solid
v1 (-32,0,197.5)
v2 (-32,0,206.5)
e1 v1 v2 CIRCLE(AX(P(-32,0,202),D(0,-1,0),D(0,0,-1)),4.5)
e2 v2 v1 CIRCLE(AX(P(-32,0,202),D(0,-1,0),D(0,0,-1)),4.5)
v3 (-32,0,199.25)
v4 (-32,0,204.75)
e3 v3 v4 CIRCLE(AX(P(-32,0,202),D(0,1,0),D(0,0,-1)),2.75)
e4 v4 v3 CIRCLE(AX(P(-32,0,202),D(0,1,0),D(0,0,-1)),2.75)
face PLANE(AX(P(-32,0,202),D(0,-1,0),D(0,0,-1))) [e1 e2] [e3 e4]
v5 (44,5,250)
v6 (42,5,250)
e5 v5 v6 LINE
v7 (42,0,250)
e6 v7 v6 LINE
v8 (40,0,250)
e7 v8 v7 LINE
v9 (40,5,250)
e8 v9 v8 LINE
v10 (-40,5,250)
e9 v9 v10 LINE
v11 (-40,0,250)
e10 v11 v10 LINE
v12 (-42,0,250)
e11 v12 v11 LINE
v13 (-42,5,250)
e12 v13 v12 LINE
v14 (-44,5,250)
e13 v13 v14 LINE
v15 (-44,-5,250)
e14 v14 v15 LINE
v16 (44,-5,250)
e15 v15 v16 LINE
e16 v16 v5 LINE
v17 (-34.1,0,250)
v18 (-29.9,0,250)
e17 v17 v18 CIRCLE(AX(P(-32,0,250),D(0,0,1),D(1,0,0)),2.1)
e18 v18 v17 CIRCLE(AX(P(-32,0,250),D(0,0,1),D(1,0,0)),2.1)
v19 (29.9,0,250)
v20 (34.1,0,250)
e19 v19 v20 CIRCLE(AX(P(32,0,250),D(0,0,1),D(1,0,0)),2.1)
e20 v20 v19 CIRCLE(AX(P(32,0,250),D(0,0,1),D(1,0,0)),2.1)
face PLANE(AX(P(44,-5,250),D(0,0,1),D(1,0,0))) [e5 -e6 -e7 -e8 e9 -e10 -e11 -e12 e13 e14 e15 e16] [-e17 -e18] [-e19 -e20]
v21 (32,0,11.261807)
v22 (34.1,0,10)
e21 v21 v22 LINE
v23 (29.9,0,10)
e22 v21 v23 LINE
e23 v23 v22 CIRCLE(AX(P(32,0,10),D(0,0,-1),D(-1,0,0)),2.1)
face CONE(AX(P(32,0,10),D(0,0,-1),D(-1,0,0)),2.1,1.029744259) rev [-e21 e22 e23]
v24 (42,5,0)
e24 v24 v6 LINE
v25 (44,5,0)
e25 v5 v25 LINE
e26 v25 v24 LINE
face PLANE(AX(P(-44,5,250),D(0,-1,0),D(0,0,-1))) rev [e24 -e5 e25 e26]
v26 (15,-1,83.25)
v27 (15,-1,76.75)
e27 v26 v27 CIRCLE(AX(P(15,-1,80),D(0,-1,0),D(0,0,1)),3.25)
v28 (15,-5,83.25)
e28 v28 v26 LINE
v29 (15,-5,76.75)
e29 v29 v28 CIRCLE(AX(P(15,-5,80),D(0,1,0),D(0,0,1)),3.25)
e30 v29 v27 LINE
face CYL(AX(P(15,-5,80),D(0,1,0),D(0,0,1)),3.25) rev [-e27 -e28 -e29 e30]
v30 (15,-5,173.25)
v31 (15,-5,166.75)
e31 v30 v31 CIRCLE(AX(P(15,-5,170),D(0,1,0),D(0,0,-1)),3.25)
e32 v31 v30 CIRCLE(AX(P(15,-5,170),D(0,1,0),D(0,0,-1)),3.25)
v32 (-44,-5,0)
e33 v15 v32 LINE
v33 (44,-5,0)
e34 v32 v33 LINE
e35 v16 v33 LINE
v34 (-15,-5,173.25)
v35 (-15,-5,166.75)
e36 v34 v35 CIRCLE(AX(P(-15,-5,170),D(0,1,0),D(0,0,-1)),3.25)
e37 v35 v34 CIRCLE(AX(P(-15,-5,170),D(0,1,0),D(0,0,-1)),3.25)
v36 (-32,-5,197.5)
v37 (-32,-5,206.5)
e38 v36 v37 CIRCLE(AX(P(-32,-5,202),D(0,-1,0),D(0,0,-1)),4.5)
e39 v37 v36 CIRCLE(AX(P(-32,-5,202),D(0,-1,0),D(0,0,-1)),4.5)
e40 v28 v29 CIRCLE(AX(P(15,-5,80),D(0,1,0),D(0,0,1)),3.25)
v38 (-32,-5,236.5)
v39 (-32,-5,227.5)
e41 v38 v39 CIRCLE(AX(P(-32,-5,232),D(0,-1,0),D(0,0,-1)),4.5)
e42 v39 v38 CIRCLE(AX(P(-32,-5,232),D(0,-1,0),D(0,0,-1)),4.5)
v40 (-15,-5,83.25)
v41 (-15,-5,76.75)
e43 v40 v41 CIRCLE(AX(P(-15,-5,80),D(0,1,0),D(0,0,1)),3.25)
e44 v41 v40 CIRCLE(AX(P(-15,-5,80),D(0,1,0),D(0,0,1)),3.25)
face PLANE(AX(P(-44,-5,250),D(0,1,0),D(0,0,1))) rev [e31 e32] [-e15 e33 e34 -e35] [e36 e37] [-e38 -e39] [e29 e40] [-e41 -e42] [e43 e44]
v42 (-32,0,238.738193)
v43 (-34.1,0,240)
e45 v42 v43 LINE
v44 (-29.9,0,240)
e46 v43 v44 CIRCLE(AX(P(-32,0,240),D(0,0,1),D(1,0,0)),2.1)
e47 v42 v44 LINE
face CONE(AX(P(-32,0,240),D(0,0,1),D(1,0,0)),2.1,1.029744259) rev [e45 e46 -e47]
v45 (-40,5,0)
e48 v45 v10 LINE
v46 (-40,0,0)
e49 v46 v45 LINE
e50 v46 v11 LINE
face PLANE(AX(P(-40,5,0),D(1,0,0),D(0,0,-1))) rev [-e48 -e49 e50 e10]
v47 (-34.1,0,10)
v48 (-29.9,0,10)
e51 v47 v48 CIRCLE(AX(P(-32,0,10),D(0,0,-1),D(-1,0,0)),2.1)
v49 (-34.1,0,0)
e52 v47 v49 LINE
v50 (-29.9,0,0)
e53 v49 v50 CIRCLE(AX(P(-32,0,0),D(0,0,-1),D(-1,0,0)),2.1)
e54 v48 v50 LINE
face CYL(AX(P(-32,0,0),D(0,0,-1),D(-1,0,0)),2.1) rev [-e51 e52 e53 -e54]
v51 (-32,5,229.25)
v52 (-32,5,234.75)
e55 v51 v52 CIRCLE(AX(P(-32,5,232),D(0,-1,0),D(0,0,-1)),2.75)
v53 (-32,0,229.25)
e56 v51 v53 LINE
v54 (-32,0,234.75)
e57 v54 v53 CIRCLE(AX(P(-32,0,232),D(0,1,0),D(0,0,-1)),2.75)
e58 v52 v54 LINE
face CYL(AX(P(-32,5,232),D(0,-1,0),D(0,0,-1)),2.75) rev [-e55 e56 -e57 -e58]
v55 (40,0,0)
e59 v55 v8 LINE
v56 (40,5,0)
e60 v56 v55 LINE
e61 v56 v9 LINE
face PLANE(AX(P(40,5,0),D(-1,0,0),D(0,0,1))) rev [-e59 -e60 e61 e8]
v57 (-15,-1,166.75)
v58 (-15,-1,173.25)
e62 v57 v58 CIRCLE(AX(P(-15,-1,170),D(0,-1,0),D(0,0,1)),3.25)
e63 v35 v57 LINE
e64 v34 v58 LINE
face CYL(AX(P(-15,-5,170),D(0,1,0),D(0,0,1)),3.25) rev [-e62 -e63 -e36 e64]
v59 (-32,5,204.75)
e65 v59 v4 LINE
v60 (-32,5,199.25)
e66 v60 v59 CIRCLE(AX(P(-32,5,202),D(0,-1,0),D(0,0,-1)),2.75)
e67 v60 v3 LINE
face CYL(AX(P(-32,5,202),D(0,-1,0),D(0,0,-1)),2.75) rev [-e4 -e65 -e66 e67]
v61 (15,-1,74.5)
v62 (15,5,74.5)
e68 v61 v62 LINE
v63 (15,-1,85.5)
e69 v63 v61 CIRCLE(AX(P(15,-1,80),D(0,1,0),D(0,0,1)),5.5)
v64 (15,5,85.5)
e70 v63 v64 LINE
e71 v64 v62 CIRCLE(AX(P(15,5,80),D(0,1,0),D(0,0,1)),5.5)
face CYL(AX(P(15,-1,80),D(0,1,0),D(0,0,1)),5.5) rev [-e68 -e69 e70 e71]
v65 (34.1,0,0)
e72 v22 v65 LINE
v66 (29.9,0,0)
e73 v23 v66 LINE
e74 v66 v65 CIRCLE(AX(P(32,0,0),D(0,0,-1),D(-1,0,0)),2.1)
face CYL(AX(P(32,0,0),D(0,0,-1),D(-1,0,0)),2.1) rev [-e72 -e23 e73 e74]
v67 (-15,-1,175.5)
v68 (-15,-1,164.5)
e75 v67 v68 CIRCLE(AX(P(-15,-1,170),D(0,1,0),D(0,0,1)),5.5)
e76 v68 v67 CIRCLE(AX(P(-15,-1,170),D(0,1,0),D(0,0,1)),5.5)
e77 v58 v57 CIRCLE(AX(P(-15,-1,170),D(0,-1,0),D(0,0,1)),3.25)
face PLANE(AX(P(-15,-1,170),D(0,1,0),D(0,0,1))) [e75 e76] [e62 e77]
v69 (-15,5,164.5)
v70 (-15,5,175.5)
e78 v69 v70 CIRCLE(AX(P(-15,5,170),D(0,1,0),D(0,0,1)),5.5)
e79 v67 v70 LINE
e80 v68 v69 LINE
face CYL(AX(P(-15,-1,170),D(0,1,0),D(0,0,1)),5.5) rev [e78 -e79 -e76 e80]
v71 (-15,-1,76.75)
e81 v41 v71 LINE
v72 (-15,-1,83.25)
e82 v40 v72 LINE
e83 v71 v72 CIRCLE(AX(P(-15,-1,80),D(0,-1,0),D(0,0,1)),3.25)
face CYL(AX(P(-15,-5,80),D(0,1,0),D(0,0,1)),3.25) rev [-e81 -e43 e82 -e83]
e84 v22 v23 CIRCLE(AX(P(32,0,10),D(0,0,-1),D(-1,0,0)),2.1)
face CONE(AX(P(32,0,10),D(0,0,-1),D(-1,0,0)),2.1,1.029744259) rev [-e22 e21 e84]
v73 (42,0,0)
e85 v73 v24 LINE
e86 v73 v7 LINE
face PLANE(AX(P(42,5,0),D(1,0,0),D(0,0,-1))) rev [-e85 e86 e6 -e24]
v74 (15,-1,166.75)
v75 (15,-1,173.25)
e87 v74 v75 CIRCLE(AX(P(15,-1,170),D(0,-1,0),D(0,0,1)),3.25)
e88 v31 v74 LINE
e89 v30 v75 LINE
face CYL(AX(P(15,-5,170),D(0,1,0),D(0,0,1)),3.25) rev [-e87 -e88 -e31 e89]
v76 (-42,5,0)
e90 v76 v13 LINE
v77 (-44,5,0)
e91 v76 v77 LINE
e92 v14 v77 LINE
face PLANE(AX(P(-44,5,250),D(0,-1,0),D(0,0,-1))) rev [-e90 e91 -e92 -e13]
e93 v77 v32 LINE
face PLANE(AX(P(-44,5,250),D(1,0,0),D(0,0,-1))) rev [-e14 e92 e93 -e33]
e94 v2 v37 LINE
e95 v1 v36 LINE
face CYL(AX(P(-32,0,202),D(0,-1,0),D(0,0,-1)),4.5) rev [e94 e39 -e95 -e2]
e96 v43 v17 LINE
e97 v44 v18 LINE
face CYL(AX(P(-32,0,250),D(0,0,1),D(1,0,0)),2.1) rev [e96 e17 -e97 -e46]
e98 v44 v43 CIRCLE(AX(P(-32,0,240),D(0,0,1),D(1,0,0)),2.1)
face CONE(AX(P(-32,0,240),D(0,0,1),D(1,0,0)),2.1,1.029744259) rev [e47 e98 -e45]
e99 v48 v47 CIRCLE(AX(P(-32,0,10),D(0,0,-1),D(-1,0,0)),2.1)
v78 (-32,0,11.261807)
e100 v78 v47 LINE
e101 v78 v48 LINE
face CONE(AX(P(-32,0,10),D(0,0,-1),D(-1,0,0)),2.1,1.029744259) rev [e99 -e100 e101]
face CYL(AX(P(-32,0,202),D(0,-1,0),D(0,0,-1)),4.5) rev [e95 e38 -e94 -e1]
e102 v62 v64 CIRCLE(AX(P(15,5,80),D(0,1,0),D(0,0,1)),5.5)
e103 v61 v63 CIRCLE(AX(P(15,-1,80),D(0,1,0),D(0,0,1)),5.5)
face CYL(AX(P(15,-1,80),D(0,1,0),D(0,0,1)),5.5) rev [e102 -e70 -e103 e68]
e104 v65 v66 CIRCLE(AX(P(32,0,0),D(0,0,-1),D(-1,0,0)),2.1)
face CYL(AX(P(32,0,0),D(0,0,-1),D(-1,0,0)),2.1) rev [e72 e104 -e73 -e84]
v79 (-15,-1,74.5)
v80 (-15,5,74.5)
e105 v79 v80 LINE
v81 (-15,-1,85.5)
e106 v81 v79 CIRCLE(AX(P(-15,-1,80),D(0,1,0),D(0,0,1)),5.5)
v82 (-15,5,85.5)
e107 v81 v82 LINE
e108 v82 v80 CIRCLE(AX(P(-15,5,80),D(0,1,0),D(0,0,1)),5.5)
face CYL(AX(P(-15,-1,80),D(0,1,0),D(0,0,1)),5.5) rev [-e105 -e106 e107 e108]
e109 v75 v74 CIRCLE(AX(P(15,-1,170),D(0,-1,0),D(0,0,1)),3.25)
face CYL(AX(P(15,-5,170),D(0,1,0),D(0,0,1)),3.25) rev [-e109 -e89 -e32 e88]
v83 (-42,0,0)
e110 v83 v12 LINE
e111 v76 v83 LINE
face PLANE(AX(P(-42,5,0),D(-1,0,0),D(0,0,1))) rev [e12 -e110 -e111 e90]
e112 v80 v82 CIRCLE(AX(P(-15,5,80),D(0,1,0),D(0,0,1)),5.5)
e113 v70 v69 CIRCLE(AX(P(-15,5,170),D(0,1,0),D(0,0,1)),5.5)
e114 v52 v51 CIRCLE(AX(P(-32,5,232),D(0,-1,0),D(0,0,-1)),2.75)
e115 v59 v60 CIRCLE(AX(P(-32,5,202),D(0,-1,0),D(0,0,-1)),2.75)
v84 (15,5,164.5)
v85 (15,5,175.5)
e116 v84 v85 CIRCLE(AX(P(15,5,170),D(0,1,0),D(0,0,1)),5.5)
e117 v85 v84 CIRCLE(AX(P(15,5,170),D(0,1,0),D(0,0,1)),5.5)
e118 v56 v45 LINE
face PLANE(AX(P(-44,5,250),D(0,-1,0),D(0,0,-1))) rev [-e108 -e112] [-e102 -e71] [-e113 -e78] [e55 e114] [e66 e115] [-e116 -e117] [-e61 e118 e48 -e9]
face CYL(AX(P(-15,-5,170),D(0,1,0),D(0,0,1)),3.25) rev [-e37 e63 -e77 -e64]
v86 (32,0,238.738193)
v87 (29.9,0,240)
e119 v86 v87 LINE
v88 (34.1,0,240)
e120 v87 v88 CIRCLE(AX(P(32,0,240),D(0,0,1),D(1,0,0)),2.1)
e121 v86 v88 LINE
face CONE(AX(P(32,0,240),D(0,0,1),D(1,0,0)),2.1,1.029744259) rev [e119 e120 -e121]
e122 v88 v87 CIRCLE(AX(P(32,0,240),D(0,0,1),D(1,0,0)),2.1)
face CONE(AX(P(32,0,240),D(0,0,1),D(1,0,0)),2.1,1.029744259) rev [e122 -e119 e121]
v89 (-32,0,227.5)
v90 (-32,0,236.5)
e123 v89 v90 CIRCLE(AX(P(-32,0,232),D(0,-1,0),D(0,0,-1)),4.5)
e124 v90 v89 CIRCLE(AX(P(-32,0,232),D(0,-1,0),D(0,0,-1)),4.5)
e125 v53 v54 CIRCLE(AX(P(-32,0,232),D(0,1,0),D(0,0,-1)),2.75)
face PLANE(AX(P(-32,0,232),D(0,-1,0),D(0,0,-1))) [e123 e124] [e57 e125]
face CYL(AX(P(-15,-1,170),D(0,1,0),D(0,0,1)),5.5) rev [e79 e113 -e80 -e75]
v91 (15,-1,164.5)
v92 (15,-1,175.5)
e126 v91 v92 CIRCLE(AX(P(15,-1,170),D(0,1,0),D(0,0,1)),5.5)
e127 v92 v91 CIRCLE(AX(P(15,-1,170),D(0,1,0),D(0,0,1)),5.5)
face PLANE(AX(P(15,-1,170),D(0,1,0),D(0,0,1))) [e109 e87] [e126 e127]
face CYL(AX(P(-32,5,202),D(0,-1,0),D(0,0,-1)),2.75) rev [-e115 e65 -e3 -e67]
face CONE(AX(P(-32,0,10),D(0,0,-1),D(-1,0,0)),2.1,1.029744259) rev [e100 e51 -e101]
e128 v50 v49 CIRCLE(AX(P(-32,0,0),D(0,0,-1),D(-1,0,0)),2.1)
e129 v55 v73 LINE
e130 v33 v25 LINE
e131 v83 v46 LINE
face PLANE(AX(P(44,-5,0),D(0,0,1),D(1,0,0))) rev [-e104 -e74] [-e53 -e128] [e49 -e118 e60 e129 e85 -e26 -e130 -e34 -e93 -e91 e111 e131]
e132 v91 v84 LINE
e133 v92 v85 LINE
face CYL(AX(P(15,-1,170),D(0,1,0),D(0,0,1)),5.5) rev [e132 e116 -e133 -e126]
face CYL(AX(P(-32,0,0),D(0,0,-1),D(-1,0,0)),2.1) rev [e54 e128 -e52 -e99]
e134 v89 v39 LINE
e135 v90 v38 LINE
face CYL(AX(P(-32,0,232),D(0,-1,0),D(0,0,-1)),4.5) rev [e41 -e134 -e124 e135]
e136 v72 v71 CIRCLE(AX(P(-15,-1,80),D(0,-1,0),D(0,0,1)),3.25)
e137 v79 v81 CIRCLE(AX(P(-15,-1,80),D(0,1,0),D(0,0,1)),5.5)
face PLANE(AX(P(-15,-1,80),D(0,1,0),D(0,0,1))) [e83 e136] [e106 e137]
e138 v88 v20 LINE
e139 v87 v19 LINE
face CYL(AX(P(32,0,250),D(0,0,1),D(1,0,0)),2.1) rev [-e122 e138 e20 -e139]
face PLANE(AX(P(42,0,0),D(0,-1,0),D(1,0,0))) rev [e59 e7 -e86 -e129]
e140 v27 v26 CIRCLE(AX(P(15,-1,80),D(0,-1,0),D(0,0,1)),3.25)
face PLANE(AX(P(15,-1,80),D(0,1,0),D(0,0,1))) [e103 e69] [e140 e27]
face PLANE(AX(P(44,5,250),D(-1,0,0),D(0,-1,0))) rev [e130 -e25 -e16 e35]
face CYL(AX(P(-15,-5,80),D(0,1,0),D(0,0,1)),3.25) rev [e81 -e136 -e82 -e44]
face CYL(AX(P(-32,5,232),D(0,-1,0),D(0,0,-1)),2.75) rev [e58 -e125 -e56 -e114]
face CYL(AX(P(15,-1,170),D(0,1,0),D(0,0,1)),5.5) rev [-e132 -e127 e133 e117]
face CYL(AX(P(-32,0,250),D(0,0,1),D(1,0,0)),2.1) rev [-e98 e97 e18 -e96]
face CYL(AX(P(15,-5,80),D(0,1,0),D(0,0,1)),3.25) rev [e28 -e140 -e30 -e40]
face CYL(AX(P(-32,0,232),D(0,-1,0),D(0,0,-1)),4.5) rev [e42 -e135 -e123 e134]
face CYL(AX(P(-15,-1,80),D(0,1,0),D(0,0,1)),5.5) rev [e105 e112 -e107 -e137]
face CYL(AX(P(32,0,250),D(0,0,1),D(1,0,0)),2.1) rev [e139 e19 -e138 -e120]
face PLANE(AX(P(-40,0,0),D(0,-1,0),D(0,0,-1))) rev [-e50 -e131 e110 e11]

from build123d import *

# Parameters (mm, degrees)
SKETCH_1_W             = 88
SKETCH_1_H             = 10
EXTRUDE_1_DEPTH        = 250
SKETCH_2_W             = 2
SKETCH_2_H             = 5
CUT_EXTRUDE_1_DEPTH    = 254.891709199
HOLE_WIZARD_M5_1_D     = 4.2
HOLE_WIZARD_M5_1_DEPTH = 10
HOLE_WIZARD_M5_1_TIP   = 1.2618073
HOLE_WIZARD_M5_2_D     = 4.2
HOLE_WIZARD_M5_2_DEPTH = 10
HOLE_WIZARD_M5_2_TIP   = 1.2618073
SKETCH_7_R             = 3.25
CUT_EXTRUDE_2_DEPTH    = 255.039367028
SKETCH_8_R             = 5.5
CUT_EXTRUDE_3_DEPTH    = 6
SKETCH_9_R             = 2.75
CUT_EXTRUDE_4_DEPTH    = 255.039367028
SKETCH_10_R            = 4.5
CUT_EXTRUDE_5_DEPTH    = 5


with BuildPart() as part:
    # 草图1 → 凸台-拉伸1 (new body)
    with BuildSketch(Plane.XY):
        Rectangle(SKETCH_1_W, SKETCH_1_H)
    extrude(amount=EXTRUDE_1_DEPTH)

    # 草图2 → 切除-拉伸1 (cut, through all)
    with BuildSketch(Plane.XY.offset(250)):
        with Locations((-41, 2.5)):
            Rectangle(SKETCH_2_W, SKETCH_2_H)
        with Locations((41, 2.5)):
            Rectangle(SKETCH_2_W, SKETCH_2_H)
    extrude(amount=-CUT_EXTRUDE_1_DEPTH, mode=Mode.SUBTRACT)

    # M5 螺纹孔1
    with Locations(Plane(origin=(-32, 0, 250), x_dir=(1, 0, 0), z_dir=(0, 0, 1))):
        with Locations((0, 0), (64, 0)):
            Hole(HOLE_WIZARD_M5_1_D / 2, depth=HOLE_WIZARD_M5_1_DEPTH)
            with Locations((0, 0, -(HOLE_WIZARD_M5_1_DEPTH + HOLE_WIZARD_M5_1_TIP / 2))):  # 118° drill point
                Cone(0, HOLE_WIZARD_M5_1_D / 2, HOLE_WIZARD_M5_1_TIP, mode=Mode.SUBTRACT)

    # M5 螺纹孔2
    with Locations(Plane(origin=(32, 0, 0), x_dir=(-1, 0, 0), z_dir=(0, 0, -1))):
        with Locations((0, 0), (64, 0)):
            Hole(HOLE_WIZARD_M5_2_D / 2, depth=HOLE_WIZARD_M5_2_DEPTH)
            with Locations((0, 0, -(HOLE_WIZARD_M5_2_DEPTH + HOLE_WIZARD_M5_2_TIP / 2))):  # 118° drill point
                Cone(0, HOLE_WIZARD_M5_2_D / 2, HOLE_WIZARD_M5_2_TIP, mode=Mode.SUBTRACT)

    # 草图7 → 切除-拉伸2 (cut, through all)
    with BuildSketch(Plane(origin=(0, 5, 0), x_dir=(1, 0, 0), z_dir=(0, 1, 0))):
        with Locations(Location((-15, -80, 0), (0, 0, 270))):
            Circle(SKETCH_7_R)
        with Locations(Location((15, -80, 0), (0, 0, 270))):
            Circle(SKETCH_7_R)
        with Locations(Location((15, -170, 0), (0, 0, 90))):
            Circle(SKETCH_7_R)
        with Locations(Location((-15, -170, 0), (0, 0, 90))):
            Circle(SKETCH_7_R)
    extrude(amount=-CUT_EXTRUDE_2_DEPTH, mode=Mode.SUBTRACT)

    # 草图8 → 切除-拉伸3 (cut)
    with BuildSketch(Plane(origin=(0, 5, 0), x_dir=(1, 0, 0), z_dir=(0, 1, 0))):
        with Locations(Location((-15, -80, 0), (0, 0, 270))):
            Circle(SKETCH_8_R)
        with Locations(Location((15, -80, 0), (0, 0, 270))):
            Circle(SKETCH_8_R)
        with Locations(Location((-15, -170, 0), (0, 0, 270))):
            Circle(SKETCH_8_R)
        with Locations(Location((15, -170, 0), (0, 0, 270))):
            Circle(SKETCH_8_R)
    extrude(amount=-CUT_EXTRUDE_3_DEPTH, mode=Mode.SUBTRACT)

    # 草图9 → 切除-拉伸4 (cut, through all)
    with BuildSketch(Plane.XZ.offset(5)):
        with Locations(Location((-32, 232, 0), (0, 0, 270))):
            Circle(SKETCH_9_R)
        with Locations(Location((-32, 202, 0), (0, 0, 270))):
            Circle(SKETCH_9_R)
    extrude(amount=-CUT_EXTRUDE_4_DEPTH, mode=Mode.SUBTRACT)

    # 草图10 → 切除-拉伸5 (cut)
    with BuildSketch(Plane.XZ.offset(5)):
        with Locations(Location((-32, 232, 0), (0, 0, 270))):
            Circle(SKETCH_10_R)
        with Locations(Location((-32, 202, 0), (0, 0, 270))):
            Circle(SKETCH_10_R)
    extrude(amount=-CUT_EXTRUDE_5_DEPTH, mode=Mode.SUBTRACT)


solid = part.part
